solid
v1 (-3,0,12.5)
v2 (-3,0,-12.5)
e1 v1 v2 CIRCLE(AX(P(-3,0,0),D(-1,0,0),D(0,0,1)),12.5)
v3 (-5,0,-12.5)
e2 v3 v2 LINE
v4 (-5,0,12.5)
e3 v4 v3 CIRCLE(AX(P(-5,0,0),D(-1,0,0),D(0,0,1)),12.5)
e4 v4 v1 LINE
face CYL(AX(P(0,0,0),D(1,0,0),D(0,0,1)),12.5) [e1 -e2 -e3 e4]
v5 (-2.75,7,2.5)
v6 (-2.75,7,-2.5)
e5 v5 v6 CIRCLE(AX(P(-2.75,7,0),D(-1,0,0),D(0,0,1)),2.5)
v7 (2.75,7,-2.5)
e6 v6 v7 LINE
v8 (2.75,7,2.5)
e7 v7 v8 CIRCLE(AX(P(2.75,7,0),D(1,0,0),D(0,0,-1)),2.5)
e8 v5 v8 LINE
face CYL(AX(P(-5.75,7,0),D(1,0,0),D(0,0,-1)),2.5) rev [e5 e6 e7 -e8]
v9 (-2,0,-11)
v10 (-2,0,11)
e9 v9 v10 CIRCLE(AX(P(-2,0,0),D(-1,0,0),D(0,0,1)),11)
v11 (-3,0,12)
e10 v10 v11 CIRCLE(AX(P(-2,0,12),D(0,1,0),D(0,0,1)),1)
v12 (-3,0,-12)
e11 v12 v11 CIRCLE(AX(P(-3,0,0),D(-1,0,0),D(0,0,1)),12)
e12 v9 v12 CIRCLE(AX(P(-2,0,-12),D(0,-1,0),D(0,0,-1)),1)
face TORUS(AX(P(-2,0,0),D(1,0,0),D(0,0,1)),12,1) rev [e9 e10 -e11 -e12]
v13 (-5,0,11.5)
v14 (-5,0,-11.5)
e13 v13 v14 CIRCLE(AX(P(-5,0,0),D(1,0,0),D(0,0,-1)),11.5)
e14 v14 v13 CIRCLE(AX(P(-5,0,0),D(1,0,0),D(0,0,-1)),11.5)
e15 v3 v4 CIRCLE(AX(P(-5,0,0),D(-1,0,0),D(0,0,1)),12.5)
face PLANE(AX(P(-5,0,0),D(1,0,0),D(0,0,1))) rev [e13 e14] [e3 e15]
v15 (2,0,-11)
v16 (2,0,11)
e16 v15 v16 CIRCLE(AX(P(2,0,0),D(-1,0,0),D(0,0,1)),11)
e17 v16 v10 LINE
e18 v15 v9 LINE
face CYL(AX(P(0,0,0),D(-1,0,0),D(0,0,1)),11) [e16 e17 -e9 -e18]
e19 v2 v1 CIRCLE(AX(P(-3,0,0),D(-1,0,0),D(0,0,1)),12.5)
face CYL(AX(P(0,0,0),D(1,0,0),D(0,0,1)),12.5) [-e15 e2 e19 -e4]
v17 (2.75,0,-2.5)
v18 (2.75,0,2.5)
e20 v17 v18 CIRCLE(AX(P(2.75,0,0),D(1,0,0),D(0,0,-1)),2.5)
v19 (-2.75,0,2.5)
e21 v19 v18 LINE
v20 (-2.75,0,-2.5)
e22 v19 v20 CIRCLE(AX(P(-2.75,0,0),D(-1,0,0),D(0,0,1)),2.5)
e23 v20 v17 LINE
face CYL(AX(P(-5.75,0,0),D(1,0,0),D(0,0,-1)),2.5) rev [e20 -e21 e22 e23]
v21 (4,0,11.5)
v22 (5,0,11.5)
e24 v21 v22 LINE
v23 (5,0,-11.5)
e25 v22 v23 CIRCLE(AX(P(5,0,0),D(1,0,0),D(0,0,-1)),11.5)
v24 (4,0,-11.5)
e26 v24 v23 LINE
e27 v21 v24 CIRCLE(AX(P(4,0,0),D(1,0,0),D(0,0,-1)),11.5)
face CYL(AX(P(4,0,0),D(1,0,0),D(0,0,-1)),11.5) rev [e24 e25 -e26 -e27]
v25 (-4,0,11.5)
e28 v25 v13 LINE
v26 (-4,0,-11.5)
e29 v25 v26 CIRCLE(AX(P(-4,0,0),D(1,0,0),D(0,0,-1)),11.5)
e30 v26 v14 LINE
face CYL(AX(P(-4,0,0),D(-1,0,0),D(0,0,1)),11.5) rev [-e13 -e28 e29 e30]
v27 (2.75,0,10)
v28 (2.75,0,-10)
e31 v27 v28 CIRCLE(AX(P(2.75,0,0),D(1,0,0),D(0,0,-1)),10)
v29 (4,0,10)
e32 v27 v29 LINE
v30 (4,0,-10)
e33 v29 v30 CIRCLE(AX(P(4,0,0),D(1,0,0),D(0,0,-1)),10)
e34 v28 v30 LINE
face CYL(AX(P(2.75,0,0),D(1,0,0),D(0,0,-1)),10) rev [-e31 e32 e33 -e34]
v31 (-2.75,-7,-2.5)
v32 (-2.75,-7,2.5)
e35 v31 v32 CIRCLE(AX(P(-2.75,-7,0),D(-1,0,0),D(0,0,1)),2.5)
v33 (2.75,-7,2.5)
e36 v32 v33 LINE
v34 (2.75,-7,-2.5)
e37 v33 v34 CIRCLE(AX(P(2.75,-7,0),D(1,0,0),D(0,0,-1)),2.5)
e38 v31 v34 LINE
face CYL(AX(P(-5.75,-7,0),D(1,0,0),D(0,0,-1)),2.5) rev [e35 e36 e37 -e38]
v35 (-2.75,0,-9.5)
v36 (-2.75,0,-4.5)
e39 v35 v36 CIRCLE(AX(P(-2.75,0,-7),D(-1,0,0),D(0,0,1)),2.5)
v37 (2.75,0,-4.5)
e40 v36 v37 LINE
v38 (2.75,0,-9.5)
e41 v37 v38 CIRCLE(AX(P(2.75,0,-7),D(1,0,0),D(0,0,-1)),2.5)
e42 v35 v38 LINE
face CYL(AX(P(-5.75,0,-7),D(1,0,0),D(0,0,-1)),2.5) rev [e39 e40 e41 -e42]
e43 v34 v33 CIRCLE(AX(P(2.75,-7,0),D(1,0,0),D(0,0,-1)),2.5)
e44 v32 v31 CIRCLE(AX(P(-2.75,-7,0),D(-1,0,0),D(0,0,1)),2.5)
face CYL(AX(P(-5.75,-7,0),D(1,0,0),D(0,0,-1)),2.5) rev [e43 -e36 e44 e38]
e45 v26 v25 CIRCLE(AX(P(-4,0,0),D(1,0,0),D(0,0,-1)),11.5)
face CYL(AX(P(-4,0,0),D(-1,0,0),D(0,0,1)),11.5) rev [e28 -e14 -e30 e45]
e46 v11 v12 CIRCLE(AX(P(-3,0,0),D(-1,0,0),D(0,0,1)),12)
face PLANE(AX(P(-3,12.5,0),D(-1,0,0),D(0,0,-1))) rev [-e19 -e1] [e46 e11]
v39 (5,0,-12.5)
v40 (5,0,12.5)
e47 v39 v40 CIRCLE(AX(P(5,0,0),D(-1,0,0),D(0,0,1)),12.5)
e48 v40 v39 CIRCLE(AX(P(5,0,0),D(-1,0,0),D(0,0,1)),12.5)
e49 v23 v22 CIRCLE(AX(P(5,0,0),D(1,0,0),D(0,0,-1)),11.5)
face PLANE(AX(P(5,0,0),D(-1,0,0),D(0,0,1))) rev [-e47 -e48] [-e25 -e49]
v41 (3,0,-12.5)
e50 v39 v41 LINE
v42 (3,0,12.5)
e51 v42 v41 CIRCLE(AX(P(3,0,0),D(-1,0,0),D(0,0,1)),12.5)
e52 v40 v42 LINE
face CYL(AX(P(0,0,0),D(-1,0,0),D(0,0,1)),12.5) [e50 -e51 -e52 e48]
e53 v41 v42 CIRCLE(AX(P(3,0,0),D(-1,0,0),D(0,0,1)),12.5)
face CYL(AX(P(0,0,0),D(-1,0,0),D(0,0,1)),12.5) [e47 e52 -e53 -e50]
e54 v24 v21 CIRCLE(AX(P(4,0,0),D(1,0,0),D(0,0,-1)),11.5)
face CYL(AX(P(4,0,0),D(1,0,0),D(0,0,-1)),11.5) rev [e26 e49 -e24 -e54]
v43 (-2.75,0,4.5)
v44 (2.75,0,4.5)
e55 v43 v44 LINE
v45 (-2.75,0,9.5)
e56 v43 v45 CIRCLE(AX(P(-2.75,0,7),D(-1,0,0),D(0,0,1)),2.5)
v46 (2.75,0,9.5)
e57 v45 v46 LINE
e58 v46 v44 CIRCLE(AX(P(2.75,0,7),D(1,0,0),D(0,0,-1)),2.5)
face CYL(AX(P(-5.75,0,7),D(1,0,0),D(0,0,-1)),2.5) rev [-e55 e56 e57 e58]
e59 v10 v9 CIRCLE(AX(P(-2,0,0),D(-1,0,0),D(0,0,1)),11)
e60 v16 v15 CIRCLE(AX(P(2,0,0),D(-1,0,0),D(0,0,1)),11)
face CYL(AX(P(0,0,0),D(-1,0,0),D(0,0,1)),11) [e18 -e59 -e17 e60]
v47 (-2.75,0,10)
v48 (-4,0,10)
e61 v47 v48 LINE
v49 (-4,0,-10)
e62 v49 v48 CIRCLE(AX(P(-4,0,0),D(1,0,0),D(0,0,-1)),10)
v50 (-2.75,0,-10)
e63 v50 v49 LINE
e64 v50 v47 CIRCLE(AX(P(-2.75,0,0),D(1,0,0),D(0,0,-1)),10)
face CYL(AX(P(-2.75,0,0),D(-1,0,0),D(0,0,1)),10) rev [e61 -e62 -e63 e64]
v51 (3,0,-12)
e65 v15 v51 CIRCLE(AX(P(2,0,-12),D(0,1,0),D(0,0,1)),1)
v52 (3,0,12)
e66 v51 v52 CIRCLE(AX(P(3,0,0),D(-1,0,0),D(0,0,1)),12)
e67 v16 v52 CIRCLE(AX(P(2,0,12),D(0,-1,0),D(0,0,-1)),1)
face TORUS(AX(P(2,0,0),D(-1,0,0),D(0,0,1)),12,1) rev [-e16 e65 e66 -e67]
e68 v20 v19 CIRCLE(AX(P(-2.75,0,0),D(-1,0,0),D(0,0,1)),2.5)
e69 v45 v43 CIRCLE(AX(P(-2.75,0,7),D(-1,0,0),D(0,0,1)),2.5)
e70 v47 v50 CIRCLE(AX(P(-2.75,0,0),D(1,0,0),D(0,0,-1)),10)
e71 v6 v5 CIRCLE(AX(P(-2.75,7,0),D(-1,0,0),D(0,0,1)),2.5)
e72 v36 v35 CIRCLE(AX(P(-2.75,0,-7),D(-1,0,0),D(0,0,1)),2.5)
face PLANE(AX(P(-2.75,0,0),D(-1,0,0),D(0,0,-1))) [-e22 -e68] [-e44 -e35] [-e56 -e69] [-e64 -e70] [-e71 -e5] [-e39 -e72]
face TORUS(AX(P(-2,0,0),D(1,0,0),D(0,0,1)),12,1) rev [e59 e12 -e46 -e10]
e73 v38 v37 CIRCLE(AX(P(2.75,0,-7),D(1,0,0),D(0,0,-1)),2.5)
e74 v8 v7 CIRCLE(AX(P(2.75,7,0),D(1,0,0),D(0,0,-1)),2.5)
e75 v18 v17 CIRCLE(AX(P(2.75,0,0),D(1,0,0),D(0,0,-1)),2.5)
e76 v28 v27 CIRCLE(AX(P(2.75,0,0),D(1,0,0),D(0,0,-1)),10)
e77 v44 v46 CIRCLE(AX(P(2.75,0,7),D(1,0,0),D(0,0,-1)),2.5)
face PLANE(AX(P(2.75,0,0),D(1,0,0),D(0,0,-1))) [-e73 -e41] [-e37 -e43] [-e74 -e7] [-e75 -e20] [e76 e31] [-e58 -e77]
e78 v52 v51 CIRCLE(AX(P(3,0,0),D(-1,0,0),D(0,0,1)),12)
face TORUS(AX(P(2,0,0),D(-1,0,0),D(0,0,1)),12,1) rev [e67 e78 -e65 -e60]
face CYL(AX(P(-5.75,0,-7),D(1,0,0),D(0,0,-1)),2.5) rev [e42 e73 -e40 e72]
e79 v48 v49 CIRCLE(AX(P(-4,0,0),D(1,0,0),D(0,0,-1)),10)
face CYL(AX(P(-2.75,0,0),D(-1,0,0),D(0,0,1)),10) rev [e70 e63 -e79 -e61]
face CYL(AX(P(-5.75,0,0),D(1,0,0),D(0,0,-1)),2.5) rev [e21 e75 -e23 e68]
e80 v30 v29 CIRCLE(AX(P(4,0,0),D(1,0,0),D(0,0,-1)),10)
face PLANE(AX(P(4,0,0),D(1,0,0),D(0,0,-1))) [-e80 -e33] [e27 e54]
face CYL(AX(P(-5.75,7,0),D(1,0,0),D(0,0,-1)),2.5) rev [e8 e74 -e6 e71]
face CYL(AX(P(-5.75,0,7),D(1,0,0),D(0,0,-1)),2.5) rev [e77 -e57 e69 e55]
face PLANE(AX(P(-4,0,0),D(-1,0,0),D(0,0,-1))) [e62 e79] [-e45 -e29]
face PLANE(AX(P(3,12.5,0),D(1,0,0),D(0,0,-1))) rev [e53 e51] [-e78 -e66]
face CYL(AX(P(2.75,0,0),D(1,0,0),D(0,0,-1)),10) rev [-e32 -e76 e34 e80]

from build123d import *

# Parameters (mm, degrees)
SKETCH2_R          = 11.5
CUT_EXTRUDE1_DEPTH = 1
SKETCH3_R          = 10
CUT_EXTRUDE2_DEPTH = 1.25
SKETCH4_R          = 2.5
CUT_EXTRUDE3_DEPTH = 8.5


with BuildPart() as part:
    # Sketch1 → Revolve1 (revolve)
    with BuildSketch(Plane.XY, mode=Mode.PRIVATE) as revolve1_sk:
        with BuildLine():
            Line((0, 0), (5, 0))
            Line((5, 0), (5, 12.5))
            Line((5, 12.5), (3, 12.5))
            Line((3, 12.5), (3, 12))
            ThreePointArc((3, 12), (2.707106781, 11.292893219), (2, 11))
            Line((2, 11), (0, 11))
            Line((0, 11), (0, 0))
        make_face()
    revolve1 = revolve(revolve1_sk.sketch.rotate(Axis((0, 0, 0), (1, 0, 0)), 90), axis=Axis((0, 0, 0), (1, 0, 0)))

    # Mirror1: Revolve1 across plane
    add(revolve1.mirror(Plane(origin=(0, 0, 0), x_dir=(0, 0, 1), z_dir=(1, 0, 0))))

    # Sketch2 → Cut-Extrude1 (cut)
    with BuildSketch(Plane(origin=(5, 0, 0), x_dir=(0, 0, -1), z_dir=(1, 0, 0))):
        Circle(SKETCH2_R)
    cut_extrude1 = extrude(amount=-CUT_EXTRUDE1_DEPTH, mode=Mode.SUBTRACT)

    # Sketch3 → Cut-Extrude2 (cut)
    with BuildSketch(Plane(origin=(4, 0, 0), x_dir=(0, 0, -1), z_dir=(1, 0, 0))):
        Circle(SKETCH3_R)
    cut_extrude2 = extrude(amount=-CUT_EXTRUDE2_DEPTH, mode=Mode.SUBTRACT)

    # Mirror3: Cut-Extrude1, Cut-Extrude2 across plane
    add(cut_extrude1.mirror(Plane(origin=(0, 0, 0), x_dir=(0, 0, 1), z_dir=(1, 0, 0))), mode=Mode.SUBTRACT)
    add(cut_extrude2.mirror(Plane(origin=(0, 0, 0), x_dir=(0, 0, 1), z_dir=(1, 0, 0))), mode=Mode.SUBTRACT)

    # Sketch4 → Cut-Extrude3 (cut)
    with BuildSketch(Plane(origin=(2.75, 0, 0), x_dir=(0, 0, -1), z_dir=(1, 0, 0))):
        with Locations((0, 7)):
            Circle(SKETCH4_R)
        with Locations((7, 0)):
            Circle(SKETCH4_R)
        with Locations((0, -7)):
            Circle(SKETCH4_R)
        with Locations((-7, 0)):
            Circle(SKETCH4_R)
        Circle(SKETCH4_R)
    extrude(amount=-CUT_EXTRUDE3_DEPTH, mode=Mode.SUBTRACT)


solid = part.part
